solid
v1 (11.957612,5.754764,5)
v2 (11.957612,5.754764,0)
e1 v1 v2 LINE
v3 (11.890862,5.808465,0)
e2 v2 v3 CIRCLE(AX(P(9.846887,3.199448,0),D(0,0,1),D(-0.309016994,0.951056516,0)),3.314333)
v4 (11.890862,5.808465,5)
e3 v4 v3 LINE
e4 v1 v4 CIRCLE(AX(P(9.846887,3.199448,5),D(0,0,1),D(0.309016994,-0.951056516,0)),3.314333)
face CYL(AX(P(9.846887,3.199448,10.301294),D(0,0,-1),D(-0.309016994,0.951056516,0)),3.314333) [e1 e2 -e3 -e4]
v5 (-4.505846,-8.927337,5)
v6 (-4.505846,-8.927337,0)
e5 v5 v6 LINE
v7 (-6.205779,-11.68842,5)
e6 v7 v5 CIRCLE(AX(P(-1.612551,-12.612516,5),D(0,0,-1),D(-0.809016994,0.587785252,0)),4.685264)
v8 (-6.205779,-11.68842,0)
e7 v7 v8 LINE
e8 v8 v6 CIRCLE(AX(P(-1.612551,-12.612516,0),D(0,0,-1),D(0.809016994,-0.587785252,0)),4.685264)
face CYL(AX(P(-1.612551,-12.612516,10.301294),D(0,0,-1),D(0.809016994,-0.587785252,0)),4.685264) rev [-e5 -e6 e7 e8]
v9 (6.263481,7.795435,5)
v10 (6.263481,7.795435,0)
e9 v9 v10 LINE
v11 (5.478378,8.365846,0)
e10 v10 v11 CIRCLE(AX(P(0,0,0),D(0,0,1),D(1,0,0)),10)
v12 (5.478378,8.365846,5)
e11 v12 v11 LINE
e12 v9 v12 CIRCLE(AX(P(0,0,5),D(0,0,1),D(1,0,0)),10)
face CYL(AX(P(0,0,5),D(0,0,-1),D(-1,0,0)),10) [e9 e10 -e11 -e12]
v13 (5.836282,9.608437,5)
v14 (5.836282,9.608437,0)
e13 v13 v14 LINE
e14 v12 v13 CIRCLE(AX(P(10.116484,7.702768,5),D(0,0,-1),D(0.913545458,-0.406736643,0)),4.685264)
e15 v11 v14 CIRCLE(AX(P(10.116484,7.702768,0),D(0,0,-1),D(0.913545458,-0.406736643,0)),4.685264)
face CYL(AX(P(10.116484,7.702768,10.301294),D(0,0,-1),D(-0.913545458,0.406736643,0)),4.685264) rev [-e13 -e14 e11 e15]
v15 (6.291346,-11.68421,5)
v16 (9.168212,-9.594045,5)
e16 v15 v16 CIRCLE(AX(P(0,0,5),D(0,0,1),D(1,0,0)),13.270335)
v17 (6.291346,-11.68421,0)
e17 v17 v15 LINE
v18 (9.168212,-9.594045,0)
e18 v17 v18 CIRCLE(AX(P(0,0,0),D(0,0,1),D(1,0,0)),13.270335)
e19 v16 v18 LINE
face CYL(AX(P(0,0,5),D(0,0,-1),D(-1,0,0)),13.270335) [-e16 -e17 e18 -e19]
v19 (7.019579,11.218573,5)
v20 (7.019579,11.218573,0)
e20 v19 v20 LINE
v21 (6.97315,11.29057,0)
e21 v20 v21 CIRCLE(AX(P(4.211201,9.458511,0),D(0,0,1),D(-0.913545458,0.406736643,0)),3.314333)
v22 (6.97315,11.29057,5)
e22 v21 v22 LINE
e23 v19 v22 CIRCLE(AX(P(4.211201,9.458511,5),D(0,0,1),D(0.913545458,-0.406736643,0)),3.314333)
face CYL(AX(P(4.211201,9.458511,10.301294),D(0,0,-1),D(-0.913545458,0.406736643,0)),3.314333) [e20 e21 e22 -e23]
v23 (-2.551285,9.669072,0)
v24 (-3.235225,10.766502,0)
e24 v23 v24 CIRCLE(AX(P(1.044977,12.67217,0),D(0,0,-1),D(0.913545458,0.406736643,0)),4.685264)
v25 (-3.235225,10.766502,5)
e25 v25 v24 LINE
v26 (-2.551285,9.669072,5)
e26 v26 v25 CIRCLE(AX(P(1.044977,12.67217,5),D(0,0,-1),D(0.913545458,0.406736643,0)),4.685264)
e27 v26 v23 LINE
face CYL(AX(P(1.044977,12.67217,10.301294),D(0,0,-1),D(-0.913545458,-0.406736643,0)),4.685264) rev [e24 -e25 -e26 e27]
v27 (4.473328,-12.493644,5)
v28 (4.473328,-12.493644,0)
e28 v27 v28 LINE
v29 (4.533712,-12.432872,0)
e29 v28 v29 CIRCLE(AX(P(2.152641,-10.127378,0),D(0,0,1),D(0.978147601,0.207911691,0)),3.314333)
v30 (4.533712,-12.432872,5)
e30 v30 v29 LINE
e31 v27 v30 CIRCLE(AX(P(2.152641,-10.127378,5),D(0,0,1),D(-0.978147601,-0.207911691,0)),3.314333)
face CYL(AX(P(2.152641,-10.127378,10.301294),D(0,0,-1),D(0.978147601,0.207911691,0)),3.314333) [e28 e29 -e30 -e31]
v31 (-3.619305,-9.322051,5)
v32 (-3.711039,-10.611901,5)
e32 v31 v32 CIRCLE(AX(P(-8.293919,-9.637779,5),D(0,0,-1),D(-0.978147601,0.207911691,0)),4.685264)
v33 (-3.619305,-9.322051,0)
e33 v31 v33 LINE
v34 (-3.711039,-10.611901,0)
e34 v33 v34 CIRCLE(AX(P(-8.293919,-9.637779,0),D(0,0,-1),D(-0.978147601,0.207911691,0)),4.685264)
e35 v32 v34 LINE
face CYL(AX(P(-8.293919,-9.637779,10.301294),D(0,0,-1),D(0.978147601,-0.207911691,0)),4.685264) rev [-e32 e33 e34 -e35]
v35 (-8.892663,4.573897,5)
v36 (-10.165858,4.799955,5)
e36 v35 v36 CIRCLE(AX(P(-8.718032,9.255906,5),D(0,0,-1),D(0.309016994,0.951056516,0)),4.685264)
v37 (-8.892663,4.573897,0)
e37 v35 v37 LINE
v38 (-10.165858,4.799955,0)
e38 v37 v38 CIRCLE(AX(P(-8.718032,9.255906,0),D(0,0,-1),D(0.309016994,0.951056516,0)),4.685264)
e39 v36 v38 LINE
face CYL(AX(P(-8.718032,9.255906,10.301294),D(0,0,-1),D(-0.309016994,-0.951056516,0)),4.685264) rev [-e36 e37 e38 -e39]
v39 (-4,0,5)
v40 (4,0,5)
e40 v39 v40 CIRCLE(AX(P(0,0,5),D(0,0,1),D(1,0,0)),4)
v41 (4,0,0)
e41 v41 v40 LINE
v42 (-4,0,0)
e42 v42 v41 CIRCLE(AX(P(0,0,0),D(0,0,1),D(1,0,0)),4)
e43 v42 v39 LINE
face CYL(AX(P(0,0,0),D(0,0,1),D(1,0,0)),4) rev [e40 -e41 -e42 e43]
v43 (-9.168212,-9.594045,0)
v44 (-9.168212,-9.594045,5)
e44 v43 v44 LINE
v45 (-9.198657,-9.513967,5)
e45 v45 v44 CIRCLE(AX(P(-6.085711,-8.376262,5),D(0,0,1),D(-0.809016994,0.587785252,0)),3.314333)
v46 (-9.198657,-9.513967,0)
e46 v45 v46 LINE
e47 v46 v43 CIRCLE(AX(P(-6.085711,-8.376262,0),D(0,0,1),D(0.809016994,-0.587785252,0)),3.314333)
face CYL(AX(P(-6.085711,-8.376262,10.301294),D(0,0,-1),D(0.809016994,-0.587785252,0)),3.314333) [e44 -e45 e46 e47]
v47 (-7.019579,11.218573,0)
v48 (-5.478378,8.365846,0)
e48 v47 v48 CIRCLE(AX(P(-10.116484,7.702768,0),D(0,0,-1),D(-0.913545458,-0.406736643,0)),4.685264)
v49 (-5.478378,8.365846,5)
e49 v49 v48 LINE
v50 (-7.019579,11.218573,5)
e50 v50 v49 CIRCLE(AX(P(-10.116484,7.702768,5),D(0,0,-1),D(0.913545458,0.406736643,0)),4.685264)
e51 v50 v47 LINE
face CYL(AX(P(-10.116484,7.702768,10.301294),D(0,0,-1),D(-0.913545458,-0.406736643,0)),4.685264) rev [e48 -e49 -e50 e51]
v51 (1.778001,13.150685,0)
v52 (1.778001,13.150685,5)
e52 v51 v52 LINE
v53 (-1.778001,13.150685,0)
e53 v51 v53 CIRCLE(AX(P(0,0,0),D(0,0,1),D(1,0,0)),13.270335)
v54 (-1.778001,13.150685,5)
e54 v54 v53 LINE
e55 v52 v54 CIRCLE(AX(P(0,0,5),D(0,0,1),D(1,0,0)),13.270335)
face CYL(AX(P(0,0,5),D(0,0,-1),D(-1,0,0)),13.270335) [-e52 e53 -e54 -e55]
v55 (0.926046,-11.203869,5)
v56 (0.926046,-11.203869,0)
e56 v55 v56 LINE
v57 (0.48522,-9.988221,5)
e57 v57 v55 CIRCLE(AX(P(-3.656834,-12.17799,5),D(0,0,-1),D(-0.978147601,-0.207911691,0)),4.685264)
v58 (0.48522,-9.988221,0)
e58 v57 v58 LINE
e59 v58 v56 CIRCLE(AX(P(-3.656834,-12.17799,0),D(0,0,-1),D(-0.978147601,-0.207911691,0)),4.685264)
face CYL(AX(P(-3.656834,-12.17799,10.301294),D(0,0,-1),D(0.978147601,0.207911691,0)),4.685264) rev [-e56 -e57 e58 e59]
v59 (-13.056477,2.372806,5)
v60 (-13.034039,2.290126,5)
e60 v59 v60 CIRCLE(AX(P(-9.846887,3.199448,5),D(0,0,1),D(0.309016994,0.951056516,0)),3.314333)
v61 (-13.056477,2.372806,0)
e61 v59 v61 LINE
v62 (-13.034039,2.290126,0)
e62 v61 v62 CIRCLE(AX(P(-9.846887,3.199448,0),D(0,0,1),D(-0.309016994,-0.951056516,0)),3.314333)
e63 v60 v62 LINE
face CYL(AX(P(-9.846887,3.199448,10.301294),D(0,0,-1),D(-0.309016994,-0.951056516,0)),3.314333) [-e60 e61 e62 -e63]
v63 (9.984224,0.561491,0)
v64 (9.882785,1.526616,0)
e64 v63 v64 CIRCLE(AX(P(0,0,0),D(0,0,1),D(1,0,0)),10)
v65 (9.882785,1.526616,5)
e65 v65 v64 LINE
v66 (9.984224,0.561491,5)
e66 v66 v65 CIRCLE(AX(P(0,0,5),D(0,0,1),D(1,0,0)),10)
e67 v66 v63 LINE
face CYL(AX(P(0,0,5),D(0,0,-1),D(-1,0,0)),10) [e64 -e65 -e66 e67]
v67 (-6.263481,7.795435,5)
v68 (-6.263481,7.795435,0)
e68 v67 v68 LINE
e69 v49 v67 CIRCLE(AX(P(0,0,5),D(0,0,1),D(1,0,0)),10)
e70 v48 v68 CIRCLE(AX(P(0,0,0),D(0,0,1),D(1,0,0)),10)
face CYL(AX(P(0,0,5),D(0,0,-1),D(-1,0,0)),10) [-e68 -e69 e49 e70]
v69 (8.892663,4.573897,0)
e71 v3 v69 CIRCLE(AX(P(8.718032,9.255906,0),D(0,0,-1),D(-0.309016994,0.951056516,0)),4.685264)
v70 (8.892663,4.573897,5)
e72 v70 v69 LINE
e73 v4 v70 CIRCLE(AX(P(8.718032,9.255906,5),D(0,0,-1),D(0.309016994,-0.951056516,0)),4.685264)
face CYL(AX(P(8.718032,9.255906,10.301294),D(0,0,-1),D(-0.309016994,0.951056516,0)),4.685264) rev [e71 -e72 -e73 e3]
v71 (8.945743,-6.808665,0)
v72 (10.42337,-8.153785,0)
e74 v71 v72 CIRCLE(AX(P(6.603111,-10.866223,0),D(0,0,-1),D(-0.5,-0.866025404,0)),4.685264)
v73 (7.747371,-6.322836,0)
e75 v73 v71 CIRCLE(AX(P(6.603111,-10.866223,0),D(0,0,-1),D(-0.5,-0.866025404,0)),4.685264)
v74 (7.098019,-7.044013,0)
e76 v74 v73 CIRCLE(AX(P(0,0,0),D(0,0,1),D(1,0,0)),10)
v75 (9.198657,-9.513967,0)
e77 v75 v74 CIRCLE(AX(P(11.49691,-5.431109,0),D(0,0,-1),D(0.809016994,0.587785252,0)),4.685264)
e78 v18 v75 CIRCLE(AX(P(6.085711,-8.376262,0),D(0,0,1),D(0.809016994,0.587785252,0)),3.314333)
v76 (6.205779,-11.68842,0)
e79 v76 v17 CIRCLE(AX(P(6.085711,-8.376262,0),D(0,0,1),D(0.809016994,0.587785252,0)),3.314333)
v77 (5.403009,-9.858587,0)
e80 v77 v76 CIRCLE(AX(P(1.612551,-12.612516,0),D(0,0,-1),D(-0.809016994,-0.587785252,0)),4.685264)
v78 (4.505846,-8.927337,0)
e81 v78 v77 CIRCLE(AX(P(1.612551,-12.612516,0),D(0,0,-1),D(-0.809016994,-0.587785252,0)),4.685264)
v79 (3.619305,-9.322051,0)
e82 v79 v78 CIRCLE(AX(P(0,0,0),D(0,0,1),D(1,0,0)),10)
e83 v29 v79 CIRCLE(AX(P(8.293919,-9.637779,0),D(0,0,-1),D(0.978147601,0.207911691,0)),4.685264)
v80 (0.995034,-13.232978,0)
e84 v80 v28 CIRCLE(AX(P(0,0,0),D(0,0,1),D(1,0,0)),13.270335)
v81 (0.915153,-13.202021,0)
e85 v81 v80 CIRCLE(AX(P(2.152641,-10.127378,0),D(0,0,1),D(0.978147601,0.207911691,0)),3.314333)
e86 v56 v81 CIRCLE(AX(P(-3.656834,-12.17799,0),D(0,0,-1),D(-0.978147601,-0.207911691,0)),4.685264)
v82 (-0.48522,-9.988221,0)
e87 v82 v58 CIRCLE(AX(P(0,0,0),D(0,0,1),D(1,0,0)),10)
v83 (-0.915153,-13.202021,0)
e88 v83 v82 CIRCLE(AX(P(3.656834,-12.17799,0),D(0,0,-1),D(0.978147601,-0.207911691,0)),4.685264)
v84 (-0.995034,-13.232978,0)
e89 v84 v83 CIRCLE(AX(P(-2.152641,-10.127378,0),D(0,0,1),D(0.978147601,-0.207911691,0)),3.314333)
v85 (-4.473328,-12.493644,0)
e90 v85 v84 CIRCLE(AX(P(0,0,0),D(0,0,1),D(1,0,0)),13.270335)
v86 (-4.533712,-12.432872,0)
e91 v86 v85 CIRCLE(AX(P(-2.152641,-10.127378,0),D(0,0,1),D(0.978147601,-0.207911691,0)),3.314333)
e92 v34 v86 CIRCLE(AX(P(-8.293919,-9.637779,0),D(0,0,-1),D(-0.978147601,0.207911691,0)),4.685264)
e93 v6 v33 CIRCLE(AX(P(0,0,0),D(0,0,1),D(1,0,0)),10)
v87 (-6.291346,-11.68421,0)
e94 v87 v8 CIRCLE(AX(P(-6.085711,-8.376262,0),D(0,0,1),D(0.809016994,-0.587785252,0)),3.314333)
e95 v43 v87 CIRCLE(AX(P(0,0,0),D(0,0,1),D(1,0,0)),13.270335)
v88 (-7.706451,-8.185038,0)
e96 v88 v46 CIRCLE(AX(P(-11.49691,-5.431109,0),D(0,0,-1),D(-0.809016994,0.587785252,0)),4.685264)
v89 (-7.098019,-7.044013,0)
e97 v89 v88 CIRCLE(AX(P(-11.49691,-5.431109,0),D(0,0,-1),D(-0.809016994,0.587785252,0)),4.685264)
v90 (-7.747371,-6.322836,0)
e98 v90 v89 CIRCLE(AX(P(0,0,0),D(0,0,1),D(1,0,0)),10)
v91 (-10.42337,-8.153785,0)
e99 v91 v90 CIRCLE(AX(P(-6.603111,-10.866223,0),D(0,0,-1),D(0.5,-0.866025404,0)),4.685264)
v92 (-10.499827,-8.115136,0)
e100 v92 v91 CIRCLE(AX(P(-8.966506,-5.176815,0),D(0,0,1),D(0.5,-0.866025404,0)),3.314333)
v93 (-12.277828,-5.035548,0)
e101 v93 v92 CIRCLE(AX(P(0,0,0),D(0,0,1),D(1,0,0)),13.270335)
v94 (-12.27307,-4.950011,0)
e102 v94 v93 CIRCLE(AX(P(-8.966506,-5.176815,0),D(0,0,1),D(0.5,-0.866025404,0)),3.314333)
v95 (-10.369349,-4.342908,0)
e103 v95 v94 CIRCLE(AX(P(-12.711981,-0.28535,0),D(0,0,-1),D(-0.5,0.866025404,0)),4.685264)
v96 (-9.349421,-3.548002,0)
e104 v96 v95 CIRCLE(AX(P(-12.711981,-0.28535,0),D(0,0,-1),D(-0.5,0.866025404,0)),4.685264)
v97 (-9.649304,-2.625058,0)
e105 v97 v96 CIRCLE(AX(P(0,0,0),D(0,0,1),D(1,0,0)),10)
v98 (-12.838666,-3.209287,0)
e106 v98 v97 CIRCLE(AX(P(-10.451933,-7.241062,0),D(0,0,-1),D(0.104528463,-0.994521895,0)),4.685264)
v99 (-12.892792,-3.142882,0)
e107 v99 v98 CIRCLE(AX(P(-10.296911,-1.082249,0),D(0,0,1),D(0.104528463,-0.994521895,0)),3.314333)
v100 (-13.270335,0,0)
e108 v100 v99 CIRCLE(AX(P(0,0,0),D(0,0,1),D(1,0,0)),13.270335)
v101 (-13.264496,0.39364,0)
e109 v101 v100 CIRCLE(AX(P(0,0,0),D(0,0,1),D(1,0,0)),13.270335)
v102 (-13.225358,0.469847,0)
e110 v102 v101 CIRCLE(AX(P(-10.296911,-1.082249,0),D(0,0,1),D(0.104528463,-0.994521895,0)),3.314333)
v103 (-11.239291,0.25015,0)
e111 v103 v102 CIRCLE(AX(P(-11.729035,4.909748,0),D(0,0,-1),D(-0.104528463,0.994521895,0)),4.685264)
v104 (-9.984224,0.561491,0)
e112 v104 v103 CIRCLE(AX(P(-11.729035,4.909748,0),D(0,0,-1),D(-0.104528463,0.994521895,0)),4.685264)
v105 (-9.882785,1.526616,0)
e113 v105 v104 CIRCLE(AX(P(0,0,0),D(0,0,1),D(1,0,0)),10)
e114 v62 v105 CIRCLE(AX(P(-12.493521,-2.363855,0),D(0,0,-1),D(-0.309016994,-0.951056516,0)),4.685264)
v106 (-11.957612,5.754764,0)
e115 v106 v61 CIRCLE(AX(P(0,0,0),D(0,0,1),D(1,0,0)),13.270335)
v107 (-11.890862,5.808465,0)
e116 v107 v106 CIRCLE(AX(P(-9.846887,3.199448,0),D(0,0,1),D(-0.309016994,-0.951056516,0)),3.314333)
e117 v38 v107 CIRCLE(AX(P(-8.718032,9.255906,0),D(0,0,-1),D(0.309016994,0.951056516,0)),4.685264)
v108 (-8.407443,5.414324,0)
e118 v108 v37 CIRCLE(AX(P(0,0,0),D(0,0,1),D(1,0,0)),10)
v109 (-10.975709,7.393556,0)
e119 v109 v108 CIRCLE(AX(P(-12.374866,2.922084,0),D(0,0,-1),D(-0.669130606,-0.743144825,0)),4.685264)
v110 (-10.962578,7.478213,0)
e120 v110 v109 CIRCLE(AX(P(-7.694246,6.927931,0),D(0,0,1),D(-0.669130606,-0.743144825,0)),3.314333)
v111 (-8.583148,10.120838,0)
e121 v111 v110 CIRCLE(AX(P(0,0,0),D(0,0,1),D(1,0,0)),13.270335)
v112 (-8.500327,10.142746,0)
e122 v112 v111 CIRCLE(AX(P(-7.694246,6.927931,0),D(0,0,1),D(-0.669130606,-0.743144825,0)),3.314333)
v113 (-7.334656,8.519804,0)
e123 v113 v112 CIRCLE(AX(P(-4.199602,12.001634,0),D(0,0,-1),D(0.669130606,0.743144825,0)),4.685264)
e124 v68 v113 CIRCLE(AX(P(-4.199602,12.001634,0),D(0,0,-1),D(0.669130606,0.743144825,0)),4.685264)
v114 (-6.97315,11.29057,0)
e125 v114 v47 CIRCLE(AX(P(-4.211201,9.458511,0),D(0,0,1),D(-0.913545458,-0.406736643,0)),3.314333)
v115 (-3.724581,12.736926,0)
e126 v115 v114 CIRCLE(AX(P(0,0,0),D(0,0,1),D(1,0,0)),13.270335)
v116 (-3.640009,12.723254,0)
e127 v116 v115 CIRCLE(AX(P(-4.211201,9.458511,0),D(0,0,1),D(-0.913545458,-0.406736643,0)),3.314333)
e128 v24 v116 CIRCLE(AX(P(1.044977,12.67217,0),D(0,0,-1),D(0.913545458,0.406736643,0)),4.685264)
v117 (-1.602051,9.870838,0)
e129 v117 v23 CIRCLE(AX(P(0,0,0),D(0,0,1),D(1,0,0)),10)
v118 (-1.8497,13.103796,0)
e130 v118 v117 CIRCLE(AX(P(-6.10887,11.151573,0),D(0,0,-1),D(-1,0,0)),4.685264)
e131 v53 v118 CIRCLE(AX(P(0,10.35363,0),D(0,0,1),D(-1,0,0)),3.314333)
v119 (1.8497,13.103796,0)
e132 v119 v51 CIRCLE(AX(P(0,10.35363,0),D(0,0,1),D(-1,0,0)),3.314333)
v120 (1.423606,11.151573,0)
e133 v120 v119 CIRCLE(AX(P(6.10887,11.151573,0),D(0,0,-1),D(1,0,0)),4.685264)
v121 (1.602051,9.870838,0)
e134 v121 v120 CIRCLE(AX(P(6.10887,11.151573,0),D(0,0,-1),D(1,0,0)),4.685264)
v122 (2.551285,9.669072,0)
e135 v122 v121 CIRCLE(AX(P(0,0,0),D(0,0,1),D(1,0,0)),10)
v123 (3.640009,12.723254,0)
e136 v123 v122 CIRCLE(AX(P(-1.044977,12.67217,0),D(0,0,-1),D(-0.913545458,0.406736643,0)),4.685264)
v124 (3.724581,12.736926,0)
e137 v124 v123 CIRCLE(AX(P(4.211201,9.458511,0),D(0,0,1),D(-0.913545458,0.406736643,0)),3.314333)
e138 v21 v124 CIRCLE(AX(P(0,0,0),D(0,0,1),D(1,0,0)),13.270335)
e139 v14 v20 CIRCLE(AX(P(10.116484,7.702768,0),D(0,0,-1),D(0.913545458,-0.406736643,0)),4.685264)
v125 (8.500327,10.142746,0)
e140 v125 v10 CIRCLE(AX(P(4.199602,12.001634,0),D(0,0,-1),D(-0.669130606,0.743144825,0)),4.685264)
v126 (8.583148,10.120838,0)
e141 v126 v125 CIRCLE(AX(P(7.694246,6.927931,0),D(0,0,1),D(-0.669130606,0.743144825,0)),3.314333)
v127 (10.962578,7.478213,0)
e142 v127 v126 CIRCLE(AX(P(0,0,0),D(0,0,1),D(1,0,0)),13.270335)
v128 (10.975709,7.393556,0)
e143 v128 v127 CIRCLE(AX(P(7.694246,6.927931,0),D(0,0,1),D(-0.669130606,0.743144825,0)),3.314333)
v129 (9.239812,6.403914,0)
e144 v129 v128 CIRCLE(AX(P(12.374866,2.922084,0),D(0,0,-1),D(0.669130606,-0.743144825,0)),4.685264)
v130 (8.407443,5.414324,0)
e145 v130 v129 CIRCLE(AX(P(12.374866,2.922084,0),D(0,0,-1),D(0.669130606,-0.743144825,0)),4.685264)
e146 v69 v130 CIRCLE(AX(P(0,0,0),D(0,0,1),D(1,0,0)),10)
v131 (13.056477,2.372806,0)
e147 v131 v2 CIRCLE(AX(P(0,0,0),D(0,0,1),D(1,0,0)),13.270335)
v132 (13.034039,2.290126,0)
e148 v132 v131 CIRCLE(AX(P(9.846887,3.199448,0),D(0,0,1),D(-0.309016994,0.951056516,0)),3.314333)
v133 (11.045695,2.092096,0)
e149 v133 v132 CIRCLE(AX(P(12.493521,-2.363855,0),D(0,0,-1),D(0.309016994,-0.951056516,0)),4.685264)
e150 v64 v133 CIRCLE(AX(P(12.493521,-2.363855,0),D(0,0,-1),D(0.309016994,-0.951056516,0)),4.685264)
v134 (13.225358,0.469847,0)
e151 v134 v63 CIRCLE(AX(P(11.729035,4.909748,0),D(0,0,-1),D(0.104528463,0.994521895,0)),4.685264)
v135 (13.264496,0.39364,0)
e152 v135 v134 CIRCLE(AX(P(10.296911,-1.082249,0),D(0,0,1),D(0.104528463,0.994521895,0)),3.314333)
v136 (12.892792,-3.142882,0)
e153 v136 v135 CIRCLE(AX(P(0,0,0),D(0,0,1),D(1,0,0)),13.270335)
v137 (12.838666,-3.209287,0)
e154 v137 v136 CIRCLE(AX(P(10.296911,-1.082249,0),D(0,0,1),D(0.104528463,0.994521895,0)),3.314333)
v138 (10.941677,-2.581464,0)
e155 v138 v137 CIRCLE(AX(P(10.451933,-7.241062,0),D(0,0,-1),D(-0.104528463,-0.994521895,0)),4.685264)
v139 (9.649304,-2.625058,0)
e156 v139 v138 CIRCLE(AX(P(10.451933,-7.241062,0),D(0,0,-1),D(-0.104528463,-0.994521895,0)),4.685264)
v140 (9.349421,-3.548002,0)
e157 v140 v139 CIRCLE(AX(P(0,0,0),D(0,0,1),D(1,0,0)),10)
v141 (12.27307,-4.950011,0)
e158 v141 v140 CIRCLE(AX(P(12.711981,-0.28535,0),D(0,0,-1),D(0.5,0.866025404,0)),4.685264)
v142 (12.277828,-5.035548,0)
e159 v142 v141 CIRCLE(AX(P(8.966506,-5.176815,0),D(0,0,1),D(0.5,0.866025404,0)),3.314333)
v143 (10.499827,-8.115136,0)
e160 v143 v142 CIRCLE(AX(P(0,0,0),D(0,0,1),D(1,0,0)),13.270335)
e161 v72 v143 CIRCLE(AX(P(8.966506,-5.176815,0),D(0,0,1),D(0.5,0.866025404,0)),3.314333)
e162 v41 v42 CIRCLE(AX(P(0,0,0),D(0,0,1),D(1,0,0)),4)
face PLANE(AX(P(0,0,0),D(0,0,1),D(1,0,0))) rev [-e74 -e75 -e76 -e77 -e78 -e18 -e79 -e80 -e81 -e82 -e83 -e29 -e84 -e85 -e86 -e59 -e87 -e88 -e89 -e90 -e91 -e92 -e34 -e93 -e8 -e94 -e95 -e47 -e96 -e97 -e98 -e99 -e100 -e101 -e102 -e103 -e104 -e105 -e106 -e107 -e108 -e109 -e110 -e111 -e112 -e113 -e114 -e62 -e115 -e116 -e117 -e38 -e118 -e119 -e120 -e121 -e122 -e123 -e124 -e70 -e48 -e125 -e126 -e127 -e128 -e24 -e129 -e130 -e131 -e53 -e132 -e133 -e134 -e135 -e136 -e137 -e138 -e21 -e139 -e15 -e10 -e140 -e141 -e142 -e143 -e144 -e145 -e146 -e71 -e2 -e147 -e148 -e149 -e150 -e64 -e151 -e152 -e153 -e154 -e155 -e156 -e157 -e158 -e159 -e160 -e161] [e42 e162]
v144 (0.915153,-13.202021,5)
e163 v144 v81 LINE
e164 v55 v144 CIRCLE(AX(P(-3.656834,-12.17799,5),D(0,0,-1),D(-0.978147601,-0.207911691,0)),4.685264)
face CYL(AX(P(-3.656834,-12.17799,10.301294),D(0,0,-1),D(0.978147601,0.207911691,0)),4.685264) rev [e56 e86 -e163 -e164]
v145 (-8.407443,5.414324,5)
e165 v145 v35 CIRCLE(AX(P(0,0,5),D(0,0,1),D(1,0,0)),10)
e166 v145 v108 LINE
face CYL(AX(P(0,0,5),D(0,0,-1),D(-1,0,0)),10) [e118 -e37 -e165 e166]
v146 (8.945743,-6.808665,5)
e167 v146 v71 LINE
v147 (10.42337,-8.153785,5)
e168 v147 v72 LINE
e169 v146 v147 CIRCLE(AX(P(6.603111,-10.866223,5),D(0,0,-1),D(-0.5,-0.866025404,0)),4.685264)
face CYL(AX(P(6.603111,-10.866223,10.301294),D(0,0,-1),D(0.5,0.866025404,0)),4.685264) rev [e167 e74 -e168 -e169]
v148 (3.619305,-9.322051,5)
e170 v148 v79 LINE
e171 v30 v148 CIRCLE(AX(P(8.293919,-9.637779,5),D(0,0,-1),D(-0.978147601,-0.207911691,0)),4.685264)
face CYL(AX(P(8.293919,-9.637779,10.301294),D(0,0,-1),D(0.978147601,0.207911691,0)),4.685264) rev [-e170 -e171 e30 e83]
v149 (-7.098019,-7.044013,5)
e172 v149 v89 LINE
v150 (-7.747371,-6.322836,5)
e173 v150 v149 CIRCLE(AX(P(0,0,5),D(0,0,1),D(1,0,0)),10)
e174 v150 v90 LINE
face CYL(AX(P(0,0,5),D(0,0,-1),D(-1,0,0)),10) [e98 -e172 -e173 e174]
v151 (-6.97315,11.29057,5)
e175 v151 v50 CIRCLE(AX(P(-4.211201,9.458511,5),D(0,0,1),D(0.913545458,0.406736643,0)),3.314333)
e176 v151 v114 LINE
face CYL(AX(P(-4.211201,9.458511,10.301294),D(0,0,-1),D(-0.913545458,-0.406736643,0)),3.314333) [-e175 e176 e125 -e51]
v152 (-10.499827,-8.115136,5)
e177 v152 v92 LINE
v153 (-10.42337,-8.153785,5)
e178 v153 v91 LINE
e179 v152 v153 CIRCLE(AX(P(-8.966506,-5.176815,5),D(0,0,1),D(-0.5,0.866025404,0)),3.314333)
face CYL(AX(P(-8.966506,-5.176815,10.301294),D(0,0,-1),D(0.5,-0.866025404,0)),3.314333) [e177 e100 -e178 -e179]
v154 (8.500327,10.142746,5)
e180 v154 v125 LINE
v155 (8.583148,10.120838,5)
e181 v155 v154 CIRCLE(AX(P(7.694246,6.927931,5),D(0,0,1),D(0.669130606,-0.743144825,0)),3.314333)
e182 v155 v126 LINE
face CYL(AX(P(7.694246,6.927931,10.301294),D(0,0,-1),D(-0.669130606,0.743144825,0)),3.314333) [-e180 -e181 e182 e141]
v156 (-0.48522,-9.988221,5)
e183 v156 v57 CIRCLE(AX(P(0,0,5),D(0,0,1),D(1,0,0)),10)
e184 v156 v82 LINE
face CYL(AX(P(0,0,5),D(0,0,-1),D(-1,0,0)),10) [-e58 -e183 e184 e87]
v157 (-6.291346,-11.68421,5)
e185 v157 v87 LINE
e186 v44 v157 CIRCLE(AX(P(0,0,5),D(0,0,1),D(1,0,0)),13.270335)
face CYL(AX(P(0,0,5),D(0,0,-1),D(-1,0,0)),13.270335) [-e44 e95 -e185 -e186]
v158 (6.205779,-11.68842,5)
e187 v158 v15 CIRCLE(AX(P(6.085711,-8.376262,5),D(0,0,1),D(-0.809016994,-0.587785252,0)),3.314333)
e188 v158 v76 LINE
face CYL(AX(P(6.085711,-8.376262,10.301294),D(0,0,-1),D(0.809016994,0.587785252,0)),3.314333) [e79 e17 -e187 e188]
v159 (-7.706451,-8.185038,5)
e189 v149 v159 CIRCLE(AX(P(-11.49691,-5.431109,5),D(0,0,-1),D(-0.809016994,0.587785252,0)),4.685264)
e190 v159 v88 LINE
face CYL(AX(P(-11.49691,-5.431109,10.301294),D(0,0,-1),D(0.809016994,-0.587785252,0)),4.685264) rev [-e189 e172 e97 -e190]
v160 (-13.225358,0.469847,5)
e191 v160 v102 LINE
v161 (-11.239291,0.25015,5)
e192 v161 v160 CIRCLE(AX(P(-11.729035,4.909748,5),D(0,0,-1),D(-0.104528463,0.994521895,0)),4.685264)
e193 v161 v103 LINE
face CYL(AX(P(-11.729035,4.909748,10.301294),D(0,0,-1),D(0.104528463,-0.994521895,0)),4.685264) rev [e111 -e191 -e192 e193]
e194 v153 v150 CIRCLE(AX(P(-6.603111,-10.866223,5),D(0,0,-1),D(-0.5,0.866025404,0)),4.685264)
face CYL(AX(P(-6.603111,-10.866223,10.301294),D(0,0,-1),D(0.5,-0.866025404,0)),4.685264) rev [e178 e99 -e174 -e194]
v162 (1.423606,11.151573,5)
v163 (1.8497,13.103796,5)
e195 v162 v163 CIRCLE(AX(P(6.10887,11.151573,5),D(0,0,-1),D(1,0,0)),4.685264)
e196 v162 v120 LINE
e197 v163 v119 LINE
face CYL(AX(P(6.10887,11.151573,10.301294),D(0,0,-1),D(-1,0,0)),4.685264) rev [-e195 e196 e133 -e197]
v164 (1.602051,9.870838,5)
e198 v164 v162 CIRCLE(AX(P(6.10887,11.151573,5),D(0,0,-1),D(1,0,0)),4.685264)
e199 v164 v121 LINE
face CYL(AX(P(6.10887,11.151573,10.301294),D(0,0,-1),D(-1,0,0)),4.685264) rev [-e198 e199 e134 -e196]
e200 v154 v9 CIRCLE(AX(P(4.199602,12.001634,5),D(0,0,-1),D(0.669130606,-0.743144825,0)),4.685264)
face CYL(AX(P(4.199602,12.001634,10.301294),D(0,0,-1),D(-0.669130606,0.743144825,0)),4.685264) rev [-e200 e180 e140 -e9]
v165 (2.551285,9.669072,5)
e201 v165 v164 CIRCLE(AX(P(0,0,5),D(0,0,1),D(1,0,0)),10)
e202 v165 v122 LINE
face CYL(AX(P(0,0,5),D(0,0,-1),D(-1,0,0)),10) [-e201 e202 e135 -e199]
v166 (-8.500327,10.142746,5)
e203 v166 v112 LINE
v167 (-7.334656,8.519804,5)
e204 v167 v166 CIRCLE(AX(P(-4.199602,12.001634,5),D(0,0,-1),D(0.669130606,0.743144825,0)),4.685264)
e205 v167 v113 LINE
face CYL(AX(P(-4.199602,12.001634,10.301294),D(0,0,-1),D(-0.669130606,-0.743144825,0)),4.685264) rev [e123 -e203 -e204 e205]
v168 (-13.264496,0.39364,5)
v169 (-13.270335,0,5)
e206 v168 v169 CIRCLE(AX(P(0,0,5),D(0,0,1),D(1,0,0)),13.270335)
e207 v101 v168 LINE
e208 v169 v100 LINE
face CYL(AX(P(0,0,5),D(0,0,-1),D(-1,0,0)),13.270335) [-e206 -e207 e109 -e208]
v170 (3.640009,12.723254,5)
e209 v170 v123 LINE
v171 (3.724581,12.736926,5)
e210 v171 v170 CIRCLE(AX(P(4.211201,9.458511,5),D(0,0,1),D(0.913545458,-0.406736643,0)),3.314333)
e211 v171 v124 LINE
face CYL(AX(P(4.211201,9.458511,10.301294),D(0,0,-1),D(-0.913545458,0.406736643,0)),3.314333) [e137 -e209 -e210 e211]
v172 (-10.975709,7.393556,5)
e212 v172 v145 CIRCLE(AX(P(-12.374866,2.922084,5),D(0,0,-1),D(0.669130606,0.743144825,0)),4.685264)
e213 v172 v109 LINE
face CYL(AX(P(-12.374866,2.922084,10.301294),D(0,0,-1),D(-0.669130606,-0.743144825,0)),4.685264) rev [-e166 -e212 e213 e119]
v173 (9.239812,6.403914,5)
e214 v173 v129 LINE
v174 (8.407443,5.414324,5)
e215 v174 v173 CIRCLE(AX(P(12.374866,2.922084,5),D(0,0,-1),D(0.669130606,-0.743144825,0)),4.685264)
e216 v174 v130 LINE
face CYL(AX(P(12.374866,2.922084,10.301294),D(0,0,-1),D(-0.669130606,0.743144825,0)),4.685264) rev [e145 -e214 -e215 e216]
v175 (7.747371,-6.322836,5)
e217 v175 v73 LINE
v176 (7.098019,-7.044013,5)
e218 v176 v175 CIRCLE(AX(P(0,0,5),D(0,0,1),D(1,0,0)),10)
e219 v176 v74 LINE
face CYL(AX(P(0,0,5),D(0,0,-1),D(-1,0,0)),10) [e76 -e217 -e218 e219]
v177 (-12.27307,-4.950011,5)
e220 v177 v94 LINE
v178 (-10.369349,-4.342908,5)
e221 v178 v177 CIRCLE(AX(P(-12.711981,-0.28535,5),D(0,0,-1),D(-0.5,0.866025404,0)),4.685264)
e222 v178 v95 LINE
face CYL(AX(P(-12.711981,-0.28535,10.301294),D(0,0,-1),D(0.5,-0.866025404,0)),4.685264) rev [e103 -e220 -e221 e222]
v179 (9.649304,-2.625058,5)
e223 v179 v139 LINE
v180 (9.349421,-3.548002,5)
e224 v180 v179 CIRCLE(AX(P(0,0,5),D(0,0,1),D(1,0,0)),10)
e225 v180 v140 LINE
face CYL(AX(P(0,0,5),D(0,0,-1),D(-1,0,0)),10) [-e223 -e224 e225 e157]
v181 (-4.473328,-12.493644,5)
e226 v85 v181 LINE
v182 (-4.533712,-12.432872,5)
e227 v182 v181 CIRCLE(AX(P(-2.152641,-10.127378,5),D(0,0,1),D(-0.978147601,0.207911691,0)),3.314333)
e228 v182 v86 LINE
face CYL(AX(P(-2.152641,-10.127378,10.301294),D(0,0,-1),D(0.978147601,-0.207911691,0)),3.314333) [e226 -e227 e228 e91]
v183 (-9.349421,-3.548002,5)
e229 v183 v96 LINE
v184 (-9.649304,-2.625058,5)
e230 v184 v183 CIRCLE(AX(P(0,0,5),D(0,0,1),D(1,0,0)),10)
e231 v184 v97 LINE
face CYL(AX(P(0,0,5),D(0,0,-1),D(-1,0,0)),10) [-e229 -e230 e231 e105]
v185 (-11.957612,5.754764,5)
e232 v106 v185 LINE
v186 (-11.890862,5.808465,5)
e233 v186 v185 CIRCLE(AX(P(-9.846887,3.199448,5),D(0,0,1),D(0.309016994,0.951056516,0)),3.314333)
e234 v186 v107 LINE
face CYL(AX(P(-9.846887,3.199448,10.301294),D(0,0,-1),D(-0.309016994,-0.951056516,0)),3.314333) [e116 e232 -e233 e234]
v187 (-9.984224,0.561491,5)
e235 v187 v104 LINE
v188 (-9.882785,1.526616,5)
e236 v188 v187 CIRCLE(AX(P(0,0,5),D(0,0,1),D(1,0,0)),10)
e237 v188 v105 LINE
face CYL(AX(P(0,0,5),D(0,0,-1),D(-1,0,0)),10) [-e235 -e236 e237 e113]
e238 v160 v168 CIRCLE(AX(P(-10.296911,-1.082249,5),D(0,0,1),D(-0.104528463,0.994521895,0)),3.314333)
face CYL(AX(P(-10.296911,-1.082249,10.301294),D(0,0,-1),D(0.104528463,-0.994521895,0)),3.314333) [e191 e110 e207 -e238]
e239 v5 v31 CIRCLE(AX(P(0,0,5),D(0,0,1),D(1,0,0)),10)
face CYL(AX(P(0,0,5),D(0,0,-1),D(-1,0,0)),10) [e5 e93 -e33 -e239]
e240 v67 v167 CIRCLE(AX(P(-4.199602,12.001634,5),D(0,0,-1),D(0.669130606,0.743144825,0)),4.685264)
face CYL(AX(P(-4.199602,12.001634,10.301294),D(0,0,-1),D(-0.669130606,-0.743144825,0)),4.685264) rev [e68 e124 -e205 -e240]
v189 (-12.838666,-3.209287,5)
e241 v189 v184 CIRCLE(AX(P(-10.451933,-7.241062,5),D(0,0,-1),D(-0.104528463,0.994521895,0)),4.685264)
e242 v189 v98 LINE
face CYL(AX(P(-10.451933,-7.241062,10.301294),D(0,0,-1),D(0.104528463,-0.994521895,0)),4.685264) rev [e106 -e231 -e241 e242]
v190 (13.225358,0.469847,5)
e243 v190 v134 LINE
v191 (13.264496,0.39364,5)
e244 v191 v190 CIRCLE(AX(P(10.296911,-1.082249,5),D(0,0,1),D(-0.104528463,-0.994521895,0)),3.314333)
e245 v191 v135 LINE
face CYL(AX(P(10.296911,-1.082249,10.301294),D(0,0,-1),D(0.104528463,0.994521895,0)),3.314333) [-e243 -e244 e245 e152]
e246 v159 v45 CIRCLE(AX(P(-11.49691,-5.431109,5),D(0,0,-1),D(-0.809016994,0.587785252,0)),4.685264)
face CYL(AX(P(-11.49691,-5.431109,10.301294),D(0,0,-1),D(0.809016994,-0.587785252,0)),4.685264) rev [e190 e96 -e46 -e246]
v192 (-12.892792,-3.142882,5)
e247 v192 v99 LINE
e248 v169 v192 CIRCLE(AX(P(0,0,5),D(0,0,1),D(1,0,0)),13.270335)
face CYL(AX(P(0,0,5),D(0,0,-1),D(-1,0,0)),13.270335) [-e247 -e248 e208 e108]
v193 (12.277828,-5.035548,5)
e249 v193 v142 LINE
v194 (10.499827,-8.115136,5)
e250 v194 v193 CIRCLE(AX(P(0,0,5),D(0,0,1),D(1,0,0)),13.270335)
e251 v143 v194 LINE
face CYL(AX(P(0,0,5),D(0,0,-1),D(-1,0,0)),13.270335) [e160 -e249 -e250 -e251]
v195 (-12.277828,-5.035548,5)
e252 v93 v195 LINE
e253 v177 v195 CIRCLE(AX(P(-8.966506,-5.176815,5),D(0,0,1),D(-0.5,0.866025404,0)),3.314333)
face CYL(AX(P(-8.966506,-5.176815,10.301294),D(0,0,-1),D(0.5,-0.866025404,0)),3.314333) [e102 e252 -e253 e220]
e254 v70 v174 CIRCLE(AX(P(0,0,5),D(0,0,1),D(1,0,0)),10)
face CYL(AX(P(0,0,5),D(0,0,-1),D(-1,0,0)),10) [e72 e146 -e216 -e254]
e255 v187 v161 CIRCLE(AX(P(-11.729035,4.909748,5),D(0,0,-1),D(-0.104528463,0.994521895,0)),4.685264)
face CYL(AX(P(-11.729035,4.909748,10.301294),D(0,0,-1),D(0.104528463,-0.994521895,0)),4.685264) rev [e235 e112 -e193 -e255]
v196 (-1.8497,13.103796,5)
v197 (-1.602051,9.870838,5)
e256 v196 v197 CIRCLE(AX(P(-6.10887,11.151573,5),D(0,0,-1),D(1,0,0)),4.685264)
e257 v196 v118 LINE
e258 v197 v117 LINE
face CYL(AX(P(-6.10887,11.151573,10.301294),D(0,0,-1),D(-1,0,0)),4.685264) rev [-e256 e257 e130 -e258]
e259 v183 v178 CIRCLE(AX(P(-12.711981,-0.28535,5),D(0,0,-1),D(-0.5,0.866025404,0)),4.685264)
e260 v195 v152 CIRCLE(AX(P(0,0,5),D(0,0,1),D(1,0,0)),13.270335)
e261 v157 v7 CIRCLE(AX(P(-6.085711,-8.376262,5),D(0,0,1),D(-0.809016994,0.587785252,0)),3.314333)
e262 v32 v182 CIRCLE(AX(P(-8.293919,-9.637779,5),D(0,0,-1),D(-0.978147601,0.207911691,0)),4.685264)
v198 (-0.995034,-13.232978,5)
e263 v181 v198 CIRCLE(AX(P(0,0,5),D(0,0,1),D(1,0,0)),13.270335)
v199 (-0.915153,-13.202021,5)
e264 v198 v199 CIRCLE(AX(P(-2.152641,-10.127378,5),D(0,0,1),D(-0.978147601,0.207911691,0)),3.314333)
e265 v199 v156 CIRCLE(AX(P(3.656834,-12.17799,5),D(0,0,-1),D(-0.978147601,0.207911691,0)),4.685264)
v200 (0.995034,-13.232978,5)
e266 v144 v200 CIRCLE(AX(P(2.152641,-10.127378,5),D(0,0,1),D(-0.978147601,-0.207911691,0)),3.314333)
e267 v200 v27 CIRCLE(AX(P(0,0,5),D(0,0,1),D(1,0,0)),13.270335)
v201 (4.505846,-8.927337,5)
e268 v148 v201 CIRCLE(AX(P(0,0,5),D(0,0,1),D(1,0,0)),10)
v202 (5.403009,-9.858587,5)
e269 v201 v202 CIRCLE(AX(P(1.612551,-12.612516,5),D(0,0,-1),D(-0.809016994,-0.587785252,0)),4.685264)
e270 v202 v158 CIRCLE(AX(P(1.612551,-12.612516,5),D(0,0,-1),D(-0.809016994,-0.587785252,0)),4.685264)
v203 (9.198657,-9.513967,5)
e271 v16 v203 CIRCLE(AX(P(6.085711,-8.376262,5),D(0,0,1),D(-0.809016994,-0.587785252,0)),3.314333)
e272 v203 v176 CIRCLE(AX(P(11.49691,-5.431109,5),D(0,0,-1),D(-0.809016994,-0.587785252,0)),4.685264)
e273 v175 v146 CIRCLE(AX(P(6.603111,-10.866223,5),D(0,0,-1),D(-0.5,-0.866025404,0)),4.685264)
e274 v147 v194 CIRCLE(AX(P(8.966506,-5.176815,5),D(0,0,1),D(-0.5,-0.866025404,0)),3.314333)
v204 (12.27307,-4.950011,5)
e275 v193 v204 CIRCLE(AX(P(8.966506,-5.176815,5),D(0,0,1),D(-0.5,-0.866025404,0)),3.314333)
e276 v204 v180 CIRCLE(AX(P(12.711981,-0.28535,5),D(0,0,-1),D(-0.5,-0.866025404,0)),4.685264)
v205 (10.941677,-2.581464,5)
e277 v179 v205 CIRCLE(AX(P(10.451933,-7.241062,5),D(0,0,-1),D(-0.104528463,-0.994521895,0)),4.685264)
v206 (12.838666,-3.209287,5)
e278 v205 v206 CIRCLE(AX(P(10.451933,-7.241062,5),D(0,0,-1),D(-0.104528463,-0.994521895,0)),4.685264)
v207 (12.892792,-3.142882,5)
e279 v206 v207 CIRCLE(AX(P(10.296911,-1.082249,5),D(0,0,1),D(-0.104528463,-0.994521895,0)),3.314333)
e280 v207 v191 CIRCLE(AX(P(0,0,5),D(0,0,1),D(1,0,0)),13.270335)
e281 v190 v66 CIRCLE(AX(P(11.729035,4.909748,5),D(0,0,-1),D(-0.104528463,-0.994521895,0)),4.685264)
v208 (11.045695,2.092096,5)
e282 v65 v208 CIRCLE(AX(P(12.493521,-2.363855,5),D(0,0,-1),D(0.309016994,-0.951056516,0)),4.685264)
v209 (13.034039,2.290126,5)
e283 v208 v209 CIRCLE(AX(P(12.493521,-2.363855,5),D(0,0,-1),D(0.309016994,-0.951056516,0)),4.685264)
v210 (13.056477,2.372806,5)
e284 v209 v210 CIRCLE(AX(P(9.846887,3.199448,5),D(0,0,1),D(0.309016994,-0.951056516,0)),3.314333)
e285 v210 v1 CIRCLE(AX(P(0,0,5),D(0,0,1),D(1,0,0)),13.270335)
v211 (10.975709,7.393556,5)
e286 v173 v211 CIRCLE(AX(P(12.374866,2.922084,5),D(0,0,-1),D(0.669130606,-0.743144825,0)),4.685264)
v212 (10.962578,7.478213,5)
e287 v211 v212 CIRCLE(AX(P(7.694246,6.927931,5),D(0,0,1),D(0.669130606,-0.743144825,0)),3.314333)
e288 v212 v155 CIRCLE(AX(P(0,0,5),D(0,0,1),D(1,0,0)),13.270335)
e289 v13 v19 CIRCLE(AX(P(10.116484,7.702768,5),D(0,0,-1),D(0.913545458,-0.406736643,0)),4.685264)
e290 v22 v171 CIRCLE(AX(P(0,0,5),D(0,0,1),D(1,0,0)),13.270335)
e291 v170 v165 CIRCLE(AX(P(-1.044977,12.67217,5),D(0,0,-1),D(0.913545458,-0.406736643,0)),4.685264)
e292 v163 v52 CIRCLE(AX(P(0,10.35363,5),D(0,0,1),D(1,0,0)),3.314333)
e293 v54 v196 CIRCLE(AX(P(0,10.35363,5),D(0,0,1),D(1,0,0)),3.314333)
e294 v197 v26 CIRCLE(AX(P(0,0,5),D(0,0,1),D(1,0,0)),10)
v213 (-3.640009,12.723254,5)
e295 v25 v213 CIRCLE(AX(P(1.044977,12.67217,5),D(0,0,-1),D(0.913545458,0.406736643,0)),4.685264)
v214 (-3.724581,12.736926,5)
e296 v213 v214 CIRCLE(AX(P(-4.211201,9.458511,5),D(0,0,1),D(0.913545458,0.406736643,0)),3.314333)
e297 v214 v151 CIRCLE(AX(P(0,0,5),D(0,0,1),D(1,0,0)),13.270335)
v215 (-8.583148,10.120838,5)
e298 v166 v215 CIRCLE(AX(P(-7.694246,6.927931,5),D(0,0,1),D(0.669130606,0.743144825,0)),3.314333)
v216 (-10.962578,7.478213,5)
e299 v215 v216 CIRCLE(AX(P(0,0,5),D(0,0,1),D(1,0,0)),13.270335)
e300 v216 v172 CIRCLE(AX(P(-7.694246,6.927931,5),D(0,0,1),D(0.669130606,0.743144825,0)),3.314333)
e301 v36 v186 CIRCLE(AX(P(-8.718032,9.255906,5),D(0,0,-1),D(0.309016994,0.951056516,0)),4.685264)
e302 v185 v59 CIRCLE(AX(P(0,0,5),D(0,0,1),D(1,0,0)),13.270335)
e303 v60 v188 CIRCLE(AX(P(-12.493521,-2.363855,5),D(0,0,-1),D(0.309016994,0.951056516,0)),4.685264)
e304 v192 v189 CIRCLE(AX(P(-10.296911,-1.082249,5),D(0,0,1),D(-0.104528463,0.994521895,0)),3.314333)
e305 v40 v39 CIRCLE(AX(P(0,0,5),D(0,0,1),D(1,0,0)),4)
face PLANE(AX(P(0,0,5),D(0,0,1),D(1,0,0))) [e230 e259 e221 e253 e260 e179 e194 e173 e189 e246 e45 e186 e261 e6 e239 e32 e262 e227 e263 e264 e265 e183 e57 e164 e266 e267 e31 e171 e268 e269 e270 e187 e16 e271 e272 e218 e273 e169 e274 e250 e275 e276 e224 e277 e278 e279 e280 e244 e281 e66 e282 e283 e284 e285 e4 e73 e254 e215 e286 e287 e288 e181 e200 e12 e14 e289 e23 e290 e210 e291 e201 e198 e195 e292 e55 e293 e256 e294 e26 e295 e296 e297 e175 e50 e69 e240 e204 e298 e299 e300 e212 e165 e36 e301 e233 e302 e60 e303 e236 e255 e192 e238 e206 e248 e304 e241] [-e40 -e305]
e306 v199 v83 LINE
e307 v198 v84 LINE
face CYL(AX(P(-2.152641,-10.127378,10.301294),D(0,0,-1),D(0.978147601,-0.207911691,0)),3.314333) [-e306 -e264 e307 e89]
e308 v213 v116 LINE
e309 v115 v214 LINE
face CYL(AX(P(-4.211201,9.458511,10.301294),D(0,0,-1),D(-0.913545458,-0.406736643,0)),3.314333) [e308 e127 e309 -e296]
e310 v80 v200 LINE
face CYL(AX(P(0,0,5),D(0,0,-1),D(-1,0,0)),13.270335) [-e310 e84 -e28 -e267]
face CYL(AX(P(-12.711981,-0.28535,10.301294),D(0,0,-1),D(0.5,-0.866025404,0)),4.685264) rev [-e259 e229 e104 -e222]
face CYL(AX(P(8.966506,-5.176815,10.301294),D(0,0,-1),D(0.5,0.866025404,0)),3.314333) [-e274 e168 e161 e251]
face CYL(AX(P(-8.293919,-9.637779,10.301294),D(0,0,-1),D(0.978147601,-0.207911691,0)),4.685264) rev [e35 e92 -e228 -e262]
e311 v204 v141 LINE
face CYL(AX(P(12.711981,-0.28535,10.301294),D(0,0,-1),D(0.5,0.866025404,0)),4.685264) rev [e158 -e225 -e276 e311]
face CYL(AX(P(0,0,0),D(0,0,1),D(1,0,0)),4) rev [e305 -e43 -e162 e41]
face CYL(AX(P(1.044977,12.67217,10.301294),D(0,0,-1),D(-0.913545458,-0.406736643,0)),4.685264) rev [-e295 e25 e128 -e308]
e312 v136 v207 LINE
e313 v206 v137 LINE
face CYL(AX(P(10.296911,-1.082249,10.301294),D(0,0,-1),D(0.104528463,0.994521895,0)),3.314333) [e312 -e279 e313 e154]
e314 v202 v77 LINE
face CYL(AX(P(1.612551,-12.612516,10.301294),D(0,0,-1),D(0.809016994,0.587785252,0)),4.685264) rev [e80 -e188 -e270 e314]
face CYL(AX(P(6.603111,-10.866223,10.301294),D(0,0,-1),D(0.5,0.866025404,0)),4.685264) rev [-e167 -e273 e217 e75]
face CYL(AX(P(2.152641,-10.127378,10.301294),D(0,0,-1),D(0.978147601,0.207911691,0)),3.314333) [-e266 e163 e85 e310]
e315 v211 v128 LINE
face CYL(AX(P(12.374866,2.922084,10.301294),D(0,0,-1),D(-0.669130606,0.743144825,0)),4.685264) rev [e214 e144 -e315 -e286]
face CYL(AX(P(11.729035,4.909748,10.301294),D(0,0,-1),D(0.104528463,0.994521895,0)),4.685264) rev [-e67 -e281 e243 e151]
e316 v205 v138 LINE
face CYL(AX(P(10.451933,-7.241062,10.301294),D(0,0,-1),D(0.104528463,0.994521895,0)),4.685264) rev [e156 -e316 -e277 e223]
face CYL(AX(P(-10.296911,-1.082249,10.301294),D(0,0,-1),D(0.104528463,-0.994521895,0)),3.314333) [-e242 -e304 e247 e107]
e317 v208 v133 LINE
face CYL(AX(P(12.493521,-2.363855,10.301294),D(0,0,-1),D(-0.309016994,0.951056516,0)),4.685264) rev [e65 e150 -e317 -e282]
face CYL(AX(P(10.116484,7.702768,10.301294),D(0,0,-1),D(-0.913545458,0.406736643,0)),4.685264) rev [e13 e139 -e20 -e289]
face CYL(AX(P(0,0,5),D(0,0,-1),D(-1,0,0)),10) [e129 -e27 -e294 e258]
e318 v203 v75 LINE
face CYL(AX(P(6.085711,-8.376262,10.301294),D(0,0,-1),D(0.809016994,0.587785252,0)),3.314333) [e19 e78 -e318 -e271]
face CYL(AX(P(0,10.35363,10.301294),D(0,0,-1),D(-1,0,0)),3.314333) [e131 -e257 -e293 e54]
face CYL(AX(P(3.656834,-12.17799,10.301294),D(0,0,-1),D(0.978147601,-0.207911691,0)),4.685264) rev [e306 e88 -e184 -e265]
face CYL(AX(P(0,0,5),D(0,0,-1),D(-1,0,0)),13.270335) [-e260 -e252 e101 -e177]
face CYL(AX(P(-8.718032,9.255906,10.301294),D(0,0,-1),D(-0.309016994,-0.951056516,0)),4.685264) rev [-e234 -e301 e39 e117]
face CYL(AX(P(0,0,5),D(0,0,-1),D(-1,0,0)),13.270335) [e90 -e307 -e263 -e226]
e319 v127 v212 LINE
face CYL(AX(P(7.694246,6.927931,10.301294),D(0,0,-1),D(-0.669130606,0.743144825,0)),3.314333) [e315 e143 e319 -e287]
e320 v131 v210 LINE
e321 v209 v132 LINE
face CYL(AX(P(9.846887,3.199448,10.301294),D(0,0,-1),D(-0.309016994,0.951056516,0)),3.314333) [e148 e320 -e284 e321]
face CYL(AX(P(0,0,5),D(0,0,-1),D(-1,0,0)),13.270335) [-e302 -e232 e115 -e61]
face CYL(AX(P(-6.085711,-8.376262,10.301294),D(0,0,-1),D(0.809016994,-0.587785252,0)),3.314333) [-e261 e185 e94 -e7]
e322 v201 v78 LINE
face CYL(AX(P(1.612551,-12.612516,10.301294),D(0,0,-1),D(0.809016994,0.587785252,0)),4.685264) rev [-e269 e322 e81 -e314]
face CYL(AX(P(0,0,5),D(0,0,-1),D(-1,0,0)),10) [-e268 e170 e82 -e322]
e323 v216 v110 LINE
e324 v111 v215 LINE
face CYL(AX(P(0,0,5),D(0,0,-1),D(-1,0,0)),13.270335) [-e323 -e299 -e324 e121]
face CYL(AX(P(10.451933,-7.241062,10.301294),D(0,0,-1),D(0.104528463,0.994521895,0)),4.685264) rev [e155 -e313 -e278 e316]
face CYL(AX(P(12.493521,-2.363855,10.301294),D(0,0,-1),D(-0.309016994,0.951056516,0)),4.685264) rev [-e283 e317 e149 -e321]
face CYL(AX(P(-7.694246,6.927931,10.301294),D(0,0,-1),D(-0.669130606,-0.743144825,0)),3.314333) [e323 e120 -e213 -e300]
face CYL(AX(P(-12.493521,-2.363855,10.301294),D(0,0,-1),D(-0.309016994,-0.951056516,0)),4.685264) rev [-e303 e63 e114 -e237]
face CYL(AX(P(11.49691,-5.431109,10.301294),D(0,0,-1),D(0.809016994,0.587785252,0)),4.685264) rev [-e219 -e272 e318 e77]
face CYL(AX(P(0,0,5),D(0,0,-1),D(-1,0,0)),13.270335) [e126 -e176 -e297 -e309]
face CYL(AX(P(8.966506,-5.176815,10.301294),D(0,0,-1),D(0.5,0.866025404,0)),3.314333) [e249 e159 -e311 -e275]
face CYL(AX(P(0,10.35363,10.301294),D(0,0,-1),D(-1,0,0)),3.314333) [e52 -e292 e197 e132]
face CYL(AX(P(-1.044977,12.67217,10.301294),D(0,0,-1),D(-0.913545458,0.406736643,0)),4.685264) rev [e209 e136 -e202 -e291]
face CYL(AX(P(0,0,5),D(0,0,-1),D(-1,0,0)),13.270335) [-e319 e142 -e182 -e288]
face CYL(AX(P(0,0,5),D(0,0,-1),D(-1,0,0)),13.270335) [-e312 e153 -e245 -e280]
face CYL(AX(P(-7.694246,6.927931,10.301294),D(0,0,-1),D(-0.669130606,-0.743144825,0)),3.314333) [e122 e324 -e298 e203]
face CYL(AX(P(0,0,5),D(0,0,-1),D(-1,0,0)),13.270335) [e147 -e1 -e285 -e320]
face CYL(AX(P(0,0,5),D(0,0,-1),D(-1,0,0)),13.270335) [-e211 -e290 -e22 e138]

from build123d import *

# Parameters (mm, degrees)
SKETCH1_R           = 10
BOSS_EXTRUDE1_DEPTH = 5
SKETCH4_R           = 2.25
CUT_EXTRUDE2_DEPTH  = 67.5
BOSS_EXTRUDE3_DEPTH = 5
CIRPATTERN2_COUNT   = 15
SKETCH6_OUTSIDE_W   = 36.97
SKETCH6_OUTSIDE_H   = 36.858
SKETCH6_OUTSIDE_R   = 13.270335227
CUT_EXTRUDE3_DEPTH  = 20.926845935
SKETCH7_R           = 4
CUT_EXTRUDE4_DEPTH  = 20.421729945


with BuildPart() as part:
    # Sketch1 → Boss-Extrude1 (new body)
    with BuildSketch(Plane.XY):
        Circle(SKETCH1_R)
    extrude(amount=BOSS_EXTRUDE1_DEPTH)

    # Sketch4 → Cut-Extrude2 (cut, symmetric)
    with BuildSketch(Plane.XY):
        Circle(SKETCH4_R)
    extrude(amount=CUT_EXTRUDE2_DEPTH, both=True, mode=Mode.SUBTRACT)

    # Sketch5 → Boss-Extrude3 (add)
    with BuildSketch(Plane.XY):
        with BuildLine():
            ThreePointArc((1.602050877, 9.870837502), (0, 10), (-1.602050877, 9.870837502))
            ThreePointArc((-1.602050877, 9.870837502), (-1.43729136, 11.509422675), (-1.849699914, 13.103795985))
            ThreePointArc((-1.849699914, 13.103795985), (0, 13.667962875), (1.849699914, 13.103795985))
            ThreePointArc((1.849699914, 13.103795985), (1.43729136, 11.509422675), (1.602050877, 9.870837502))
        make_face()
    boss_extrude3 = extrude(amount=BOSS_EXTRUDE3_DEPTH)

    # CirPattern2: Boss-Extrude3 ×15 about axis
    cirpattern2_axis = Axis((0, 0, 0), (0, 0, 1))
    for i in range(1, CIRPATTERN2_COUNT):
        add(boss_extrude3.rotate(cirpattern2_axis, i * 360 / CIRPATTERN2_COUNT))

    # Sketch6 outside → Cut-Extrude3 (cut, through all)
    with BuildSketch(Plane.XY):
        with Locations((0, 0.113)):
            Rectangle(SKETCH6_OUTSIDE_W, SKETCH6_OUTSIDE_H)
        Circle(SKETCH6_OUTSIDE_R, mode=Mode.SUBTRACT)
    extrude(amount=CUT_EXTRUDE3_DEPTH, mode=Mode.SUBTRACT)

    # Sketch7 → Cut-Extrude4 (cut, through all)
    with BuildSketch(Plane.XY.offset(5)):
        Circle(SKETCH7_R)
    extrude(amount=-CUT_EXTRUDE4_DEPTH, mode=Mode.SUBTRACT)


solid = part.part
